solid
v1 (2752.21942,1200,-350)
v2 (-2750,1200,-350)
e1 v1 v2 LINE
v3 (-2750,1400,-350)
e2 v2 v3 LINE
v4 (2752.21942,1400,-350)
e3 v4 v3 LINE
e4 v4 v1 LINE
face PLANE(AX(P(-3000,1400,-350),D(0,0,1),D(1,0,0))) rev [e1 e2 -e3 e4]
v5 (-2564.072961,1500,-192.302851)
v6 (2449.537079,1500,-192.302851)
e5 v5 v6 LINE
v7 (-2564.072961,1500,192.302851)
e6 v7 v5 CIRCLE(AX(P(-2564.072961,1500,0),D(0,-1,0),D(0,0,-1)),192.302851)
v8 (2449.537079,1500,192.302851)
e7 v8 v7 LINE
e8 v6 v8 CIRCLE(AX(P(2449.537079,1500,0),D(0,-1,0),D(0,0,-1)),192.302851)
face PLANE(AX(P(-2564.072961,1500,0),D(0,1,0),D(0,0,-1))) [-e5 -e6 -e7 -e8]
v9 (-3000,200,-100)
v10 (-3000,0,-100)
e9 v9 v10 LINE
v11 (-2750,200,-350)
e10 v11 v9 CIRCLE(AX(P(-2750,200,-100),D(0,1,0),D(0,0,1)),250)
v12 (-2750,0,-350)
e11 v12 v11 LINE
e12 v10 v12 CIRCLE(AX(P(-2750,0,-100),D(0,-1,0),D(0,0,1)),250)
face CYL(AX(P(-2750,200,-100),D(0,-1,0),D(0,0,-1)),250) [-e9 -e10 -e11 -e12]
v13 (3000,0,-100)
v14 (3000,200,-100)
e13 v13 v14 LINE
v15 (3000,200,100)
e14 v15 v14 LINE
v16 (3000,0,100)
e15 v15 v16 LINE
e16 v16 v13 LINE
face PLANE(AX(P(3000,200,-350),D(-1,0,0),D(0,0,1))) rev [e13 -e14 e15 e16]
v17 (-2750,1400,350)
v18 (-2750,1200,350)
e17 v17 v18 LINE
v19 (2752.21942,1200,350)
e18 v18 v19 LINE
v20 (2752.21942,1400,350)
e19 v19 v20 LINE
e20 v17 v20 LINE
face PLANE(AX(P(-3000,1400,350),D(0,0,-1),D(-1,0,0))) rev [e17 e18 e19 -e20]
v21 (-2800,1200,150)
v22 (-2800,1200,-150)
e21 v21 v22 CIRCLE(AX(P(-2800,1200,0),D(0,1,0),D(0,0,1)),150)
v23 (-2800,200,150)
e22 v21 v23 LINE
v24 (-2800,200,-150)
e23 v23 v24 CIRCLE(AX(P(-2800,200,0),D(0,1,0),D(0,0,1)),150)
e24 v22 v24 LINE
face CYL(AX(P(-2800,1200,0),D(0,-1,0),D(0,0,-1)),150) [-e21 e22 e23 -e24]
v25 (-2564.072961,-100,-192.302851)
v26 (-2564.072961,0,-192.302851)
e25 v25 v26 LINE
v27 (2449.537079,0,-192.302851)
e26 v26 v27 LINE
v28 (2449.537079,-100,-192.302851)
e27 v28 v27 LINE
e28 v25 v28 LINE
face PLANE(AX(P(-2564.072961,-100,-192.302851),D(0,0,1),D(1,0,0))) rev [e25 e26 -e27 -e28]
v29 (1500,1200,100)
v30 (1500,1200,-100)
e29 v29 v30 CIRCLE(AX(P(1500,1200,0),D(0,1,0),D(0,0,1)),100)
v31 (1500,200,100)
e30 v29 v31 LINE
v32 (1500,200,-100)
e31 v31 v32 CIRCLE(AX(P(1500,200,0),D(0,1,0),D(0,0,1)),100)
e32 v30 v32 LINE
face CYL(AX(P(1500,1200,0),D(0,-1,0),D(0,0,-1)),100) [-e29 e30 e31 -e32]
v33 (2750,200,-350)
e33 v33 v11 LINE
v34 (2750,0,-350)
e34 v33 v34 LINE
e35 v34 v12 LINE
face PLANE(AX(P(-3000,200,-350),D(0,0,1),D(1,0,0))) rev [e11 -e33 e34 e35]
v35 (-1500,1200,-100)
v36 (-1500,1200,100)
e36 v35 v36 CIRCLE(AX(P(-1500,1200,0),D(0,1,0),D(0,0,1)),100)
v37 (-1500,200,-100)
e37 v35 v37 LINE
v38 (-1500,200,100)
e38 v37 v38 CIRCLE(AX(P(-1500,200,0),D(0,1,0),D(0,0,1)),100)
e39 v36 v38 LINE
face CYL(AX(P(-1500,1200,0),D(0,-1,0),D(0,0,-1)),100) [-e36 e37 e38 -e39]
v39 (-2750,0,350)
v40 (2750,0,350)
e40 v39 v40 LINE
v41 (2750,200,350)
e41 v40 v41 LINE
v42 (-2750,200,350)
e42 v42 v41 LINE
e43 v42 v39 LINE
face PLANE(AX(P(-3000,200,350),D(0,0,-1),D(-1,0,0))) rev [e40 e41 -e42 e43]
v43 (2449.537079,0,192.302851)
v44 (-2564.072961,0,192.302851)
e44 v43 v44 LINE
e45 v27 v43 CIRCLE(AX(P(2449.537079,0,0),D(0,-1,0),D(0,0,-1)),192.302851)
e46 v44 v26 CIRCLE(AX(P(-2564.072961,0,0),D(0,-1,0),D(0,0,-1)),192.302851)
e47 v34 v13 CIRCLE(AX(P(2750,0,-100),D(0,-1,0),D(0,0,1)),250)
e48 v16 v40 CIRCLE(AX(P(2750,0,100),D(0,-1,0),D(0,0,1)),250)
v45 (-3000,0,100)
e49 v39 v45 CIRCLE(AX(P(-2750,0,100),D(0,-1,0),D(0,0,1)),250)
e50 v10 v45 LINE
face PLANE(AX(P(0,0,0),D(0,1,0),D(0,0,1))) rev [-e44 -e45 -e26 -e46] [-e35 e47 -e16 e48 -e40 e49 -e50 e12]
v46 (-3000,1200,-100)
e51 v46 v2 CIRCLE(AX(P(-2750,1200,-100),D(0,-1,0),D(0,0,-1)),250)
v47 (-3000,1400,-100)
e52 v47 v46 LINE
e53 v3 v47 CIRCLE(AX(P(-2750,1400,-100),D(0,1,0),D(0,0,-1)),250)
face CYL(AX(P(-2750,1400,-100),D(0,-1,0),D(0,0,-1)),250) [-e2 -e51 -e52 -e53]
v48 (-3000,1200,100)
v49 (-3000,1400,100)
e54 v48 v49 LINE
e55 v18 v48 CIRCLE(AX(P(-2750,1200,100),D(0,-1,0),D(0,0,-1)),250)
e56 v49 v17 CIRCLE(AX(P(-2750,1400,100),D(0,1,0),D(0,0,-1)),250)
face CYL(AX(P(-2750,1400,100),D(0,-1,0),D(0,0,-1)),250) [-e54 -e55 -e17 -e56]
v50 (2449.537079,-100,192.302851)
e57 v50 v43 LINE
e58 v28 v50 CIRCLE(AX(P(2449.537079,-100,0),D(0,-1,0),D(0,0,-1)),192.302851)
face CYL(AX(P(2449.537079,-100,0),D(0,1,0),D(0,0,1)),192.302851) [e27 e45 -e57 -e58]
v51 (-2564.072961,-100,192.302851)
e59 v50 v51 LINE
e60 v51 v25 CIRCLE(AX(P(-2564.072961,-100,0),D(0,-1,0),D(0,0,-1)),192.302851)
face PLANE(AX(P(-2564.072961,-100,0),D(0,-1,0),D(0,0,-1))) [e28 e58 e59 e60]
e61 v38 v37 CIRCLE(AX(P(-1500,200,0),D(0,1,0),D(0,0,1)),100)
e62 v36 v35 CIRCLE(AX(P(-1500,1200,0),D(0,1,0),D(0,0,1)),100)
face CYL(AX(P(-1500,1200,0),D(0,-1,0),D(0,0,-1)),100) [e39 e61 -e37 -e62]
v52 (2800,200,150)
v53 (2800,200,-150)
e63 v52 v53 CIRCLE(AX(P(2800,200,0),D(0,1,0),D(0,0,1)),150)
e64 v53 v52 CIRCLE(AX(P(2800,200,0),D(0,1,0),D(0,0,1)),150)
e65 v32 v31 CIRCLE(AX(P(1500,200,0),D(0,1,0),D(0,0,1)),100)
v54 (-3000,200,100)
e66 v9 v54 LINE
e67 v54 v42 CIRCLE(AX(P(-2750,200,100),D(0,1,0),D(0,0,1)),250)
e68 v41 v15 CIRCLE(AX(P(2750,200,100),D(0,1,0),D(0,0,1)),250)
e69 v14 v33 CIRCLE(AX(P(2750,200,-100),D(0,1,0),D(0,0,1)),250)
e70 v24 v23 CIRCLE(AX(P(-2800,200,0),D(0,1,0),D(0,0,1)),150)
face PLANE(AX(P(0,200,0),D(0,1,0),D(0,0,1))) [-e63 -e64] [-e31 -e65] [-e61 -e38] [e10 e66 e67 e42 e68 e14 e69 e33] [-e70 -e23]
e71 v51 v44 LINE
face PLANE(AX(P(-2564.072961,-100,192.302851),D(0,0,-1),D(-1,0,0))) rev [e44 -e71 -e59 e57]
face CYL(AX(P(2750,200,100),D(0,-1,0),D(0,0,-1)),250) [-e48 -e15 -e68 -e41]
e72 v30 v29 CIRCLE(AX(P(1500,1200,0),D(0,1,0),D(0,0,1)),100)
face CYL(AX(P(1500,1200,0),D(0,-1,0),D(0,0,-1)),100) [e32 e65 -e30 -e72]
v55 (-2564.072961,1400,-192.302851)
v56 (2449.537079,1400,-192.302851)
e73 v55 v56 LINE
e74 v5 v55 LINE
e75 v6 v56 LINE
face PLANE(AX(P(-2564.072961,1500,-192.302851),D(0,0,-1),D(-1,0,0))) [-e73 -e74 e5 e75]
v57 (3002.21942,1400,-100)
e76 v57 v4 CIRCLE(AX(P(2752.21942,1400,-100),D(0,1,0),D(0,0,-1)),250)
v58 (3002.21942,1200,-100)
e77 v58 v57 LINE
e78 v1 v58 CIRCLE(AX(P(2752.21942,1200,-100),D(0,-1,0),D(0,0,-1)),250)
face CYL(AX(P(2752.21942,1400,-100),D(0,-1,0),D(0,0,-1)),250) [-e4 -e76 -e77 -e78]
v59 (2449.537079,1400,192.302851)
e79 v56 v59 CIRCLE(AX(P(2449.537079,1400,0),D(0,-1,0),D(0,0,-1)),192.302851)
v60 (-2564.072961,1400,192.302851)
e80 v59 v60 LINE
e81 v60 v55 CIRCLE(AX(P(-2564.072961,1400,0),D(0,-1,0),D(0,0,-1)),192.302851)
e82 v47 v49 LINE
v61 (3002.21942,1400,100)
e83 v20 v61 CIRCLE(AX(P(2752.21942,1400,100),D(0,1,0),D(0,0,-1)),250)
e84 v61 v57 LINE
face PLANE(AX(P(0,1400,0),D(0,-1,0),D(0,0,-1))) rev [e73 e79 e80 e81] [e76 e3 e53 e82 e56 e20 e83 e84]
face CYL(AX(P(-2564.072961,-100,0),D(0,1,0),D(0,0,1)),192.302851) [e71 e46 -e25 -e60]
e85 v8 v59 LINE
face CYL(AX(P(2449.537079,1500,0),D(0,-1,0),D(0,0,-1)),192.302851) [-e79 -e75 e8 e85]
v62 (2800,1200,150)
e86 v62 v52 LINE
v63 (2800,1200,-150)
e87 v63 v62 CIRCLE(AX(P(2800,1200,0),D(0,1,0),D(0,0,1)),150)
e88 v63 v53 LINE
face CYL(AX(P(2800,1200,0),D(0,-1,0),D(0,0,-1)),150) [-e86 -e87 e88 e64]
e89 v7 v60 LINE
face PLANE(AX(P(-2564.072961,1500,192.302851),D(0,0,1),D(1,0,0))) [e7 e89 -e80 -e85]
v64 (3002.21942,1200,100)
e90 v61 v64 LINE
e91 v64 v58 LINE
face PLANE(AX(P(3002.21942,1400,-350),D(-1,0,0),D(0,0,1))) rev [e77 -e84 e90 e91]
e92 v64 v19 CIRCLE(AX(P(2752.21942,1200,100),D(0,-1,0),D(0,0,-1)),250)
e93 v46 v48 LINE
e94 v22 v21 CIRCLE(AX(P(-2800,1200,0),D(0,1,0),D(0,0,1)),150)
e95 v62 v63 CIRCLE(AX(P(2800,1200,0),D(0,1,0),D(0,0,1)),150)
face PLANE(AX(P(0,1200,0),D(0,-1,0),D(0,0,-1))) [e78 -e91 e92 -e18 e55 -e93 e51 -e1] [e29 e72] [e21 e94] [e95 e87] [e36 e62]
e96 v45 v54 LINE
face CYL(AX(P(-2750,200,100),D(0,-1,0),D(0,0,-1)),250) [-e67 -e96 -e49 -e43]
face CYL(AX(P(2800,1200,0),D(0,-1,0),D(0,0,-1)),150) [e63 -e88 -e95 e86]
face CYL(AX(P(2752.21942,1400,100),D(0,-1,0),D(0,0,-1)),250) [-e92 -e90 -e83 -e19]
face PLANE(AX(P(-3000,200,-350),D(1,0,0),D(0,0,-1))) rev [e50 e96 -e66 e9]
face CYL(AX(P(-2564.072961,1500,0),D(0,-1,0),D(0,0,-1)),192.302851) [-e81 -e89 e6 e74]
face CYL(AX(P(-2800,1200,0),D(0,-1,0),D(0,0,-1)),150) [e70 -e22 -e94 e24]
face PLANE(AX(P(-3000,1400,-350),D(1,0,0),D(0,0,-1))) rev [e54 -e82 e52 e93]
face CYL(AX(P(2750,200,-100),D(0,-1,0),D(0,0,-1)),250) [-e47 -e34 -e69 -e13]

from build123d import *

# Parameters (mm, degrees)
SKETCH3_W           = 6000
SKETCH3_H           = 700
BOSS_EXTRUDE3_DEPTH = 200
SKETCH4_R           = 150
SKETCH4_R_2         = 100
BOSS_EXTRUDE4_DEPTH = 1000
SKETCH5_W           = 6002.219419971
SKETCH5_H           = 700
BOSS_EXTRUDE5_DEPTH = 200
FILLET1_R           = 250
BOSS_EXTRUDE6_DEPTH = 100


with BuildPart() as part:
    # Sketch3 → Boss-Extrude3 (new body)
    with BuildSketch(Plane(origin=(0, 0, 0), x_dir=(1, 0, 0), z_dir=(0, 1, 0))):
        Rectangle(SKETCH3_W, SKETCH3_H)
    extrude(amount=BOSS_EXTRUDE3_DEPTH)

    # Sketch4 → Boss-Extrude4 (add)
    with BuildSketch(Plane(origin=(0, 200, 0), x_dir=(1, 0, 0), z_dir=(0, 1, 0))):
        with Locations(Location((-2800, 0, 0), (0, 0, 270))):
            Circle(SKETCH4_R)
        with Locations(Location((2800, 0, 0), (0, 0, 270))):
            Circle(SKETCH4_R)
        with Locations(Location((-1500, 0, 0), (0, 0, 270))):
            Circle(SKETCH4_R_2)
        with Locations(Location((1500, 0, 0), (0, 0, 270))):
            Circle(SKETCH4_R_2)
    extrude(amount=BOSS_EXTRUDE4_DEPTH)

    # Sketch5 → Boss-Extrude5 (add)
    with BuildSketch(Plane(origin=(0, 1200, 0), x_dir=(1, 0, 0), z_dir=(0, 1, 0))):
        with Locations((1.109709986, 0)):
            Rectangle(SKETCH5_W, SKETCH5_H)
    extrude(amount=BOSS_EXTRUDE5_DEPTH)

    # Fillet1
    fillet1_edges = [part.edges().sort_by_distance(p)[0] for p in [
        (3002.219419971, 1300, -350),
        (-3000, 1300, -350),
        (-3000, 1300, 350),
        (3002.219419971, 1300, 350),
        (3000, 100, 350),
        (-3000, 100, 350),
        (-3000, 100, -350),
        (3000, 100, -350),
    ]]
    fillet(fillet1_edges, radius=FILLET1_R)

    # Sketch6 → Boss-Extrude6 (add)
    with BuildSketch(Plane.XZ):
        with BuildLine():
            Line((-2564.072960881, 192.302850828), (2449.537078564, 192.302850828))
            ThreePointArc((2449.537078564, 192.302850828), (2641.839929392, 0), (2449.537078564, -192.302850828))
            Line((2449.537078564, -192.302850828), (-2564.072960881, -192.302850828))
            ThreePointArc((-2564.072960881, -192.302850828), (-2756.375811709, 0), (-2564.072960881, 192.302850828))
        make_face()
    boss_extrude6 = extrude(amount=BOSS_EXTRUDE6_DEPTH)

    # Mirror1: Boss-Extrude6 across plane
    add(boss_extrude6.mirror(Plane.ZX.offset(700)))


solid = part.part
